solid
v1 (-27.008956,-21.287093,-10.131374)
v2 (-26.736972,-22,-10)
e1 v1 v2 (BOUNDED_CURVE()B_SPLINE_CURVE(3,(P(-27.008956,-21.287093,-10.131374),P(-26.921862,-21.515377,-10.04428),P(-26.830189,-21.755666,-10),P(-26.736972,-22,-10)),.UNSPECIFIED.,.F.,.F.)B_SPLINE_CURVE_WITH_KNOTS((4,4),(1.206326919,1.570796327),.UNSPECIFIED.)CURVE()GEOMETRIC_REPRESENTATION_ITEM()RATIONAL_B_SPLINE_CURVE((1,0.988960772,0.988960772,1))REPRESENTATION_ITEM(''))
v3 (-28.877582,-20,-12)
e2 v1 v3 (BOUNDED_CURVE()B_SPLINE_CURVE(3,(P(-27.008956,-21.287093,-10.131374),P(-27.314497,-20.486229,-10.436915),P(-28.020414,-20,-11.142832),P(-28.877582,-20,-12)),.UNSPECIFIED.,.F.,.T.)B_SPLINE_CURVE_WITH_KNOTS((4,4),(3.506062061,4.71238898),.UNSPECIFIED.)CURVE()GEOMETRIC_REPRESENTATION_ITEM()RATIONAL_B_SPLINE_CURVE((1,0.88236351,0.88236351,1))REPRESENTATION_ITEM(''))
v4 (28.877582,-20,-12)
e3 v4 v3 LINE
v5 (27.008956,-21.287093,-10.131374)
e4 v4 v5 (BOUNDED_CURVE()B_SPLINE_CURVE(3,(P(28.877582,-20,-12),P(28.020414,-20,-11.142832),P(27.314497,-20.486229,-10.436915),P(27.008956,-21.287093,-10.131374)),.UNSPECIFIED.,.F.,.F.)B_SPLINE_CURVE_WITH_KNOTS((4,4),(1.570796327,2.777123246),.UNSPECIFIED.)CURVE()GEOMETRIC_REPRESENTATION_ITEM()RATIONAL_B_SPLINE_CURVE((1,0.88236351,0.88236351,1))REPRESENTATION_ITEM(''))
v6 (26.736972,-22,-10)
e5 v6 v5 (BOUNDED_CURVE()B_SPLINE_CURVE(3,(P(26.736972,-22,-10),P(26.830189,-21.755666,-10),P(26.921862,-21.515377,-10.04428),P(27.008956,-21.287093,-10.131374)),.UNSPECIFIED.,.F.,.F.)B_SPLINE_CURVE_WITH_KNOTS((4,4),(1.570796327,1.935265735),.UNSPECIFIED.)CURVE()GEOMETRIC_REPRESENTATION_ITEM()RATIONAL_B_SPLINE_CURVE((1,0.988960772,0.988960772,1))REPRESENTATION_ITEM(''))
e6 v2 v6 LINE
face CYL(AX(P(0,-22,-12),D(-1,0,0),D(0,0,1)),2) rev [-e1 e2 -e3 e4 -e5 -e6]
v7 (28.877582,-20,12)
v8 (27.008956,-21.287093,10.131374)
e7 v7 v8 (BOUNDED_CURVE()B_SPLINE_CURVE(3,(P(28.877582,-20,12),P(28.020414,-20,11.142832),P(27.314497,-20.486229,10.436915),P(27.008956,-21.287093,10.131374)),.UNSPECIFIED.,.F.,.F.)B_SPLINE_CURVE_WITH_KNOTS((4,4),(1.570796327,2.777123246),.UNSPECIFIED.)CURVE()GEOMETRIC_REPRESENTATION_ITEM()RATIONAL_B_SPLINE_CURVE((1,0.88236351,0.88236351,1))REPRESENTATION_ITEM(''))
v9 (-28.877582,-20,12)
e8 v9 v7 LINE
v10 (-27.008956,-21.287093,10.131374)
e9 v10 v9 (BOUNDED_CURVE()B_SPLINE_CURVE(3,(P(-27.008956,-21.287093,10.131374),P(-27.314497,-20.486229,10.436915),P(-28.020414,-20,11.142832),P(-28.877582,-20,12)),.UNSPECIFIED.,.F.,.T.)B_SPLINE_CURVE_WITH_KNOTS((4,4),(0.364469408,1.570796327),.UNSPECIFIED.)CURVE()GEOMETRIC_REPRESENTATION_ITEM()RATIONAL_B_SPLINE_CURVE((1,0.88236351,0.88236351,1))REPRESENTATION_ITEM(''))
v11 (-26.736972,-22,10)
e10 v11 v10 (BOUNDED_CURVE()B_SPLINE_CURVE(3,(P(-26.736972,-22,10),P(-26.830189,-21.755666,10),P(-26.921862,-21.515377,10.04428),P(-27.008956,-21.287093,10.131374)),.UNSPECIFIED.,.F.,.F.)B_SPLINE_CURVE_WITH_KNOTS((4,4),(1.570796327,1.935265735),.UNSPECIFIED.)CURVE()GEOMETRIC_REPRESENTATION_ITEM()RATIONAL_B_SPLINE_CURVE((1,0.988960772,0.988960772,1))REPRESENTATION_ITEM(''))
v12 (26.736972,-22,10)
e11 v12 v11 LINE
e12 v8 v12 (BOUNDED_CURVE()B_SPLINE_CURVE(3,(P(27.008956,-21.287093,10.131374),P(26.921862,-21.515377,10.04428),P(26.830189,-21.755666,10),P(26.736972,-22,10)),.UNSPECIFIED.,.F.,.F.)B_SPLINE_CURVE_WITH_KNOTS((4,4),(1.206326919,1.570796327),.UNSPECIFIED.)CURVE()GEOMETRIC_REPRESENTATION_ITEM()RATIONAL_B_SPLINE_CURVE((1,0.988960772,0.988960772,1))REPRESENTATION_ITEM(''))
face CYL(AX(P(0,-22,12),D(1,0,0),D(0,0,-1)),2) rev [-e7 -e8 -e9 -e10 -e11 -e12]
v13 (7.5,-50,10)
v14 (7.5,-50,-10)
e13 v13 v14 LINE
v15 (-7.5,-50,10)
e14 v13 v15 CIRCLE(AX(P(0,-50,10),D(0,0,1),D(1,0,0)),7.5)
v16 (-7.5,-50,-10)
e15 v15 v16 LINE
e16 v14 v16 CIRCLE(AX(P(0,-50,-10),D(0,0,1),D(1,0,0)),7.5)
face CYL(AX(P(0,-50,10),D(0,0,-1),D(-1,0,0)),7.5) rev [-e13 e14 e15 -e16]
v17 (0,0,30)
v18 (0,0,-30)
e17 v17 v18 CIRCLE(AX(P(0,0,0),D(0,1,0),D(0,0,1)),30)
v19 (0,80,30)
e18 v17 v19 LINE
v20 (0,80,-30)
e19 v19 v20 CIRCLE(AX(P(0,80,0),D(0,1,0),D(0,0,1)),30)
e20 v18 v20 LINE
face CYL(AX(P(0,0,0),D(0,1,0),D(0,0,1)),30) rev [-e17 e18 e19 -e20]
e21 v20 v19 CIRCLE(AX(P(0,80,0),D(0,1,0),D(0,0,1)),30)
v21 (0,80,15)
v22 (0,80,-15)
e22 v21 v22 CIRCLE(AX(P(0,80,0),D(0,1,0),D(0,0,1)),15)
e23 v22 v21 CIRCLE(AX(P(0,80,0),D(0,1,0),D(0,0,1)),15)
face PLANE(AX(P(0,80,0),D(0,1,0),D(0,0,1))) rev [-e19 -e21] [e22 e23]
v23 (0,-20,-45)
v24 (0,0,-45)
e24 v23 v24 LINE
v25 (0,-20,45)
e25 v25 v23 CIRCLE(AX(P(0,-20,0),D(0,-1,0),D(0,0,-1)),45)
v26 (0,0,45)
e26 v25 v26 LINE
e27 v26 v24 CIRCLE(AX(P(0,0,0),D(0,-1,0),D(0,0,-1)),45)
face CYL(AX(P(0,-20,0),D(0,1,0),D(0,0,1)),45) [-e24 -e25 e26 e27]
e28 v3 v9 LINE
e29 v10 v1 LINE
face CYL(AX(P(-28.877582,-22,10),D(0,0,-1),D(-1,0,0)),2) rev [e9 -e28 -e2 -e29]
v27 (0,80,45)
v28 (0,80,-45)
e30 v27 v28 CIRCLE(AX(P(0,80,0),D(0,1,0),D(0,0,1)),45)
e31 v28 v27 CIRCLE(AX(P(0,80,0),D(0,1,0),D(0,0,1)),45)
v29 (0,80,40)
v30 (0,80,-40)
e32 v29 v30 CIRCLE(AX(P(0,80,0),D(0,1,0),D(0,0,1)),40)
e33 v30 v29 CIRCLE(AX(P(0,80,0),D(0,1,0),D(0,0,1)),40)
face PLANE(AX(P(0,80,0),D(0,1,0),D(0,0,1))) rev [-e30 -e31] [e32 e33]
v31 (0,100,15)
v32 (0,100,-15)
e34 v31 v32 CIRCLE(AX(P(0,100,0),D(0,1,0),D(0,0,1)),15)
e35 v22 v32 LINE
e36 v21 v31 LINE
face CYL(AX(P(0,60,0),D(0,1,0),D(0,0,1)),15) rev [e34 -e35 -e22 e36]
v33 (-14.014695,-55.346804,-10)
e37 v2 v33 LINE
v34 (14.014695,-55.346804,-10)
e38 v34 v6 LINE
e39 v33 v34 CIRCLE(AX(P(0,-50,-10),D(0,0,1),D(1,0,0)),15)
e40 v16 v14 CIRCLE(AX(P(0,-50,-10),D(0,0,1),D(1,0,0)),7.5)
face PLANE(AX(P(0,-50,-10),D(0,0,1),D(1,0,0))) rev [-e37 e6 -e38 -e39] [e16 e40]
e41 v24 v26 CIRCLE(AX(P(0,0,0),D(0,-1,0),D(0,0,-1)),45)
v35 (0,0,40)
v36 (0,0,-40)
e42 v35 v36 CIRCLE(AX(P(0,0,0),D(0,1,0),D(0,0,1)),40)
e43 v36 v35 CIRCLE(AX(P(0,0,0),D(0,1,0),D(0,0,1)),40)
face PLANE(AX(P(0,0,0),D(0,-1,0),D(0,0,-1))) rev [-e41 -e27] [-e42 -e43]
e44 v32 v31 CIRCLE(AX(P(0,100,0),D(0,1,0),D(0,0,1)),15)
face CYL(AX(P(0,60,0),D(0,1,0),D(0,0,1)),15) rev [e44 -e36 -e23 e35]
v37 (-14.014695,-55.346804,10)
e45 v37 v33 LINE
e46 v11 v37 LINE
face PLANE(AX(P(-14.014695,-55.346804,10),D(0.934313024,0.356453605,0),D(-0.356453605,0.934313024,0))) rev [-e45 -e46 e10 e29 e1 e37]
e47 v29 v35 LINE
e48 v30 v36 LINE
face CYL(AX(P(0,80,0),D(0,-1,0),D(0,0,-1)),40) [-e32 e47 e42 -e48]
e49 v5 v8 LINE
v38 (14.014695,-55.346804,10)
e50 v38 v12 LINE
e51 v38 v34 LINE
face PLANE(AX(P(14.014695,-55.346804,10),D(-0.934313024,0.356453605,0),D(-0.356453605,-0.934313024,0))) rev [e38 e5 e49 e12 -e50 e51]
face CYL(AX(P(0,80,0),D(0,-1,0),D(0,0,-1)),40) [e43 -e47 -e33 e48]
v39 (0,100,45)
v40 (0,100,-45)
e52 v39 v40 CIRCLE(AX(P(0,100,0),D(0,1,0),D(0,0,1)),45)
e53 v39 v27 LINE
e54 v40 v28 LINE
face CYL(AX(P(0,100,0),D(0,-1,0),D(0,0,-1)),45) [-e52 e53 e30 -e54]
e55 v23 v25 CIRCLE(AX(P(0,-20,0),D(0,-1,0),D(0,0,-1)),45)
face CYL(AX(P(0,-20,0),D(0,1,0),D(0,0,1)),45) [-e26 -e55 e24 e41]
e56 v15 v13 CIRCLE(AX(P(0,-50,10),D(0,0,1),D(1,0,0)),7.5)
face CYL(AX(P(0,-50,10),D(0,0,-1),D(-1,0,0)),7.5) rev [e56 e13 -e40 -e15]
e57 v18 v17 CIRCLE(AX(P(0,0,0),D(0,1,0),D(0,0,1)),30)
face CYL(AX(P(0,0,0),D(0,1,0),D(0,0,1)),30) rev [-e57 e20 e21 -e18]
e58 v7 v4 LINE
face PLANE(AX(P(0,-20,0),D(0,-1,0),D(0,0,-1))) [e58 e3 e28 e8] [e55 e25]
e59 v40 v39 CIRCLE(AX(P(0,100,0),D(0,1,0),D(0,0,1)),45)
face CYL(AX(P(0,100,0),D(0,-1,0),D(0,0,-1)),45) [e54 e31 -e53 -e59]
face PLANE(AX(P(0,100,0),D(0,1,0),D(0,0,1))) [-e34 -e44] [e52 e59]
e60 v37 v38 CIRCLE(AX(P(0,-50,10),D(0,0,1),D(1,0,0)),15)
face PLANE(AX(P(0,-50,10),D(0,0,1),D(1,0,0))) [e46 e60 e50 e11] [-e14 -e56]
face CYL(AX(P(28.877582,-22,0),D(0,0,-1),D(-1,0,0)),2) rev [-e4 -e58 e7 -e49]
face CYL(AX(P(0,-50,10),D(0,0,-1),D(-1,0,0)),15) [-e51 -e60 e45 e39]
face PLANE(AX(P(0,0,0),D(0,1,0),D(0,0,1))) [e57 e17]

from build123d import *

# Parameters (mm, degrees)
SKETCH_1_R          = 40
EXTRUDE_1_DEPTH     = 80
SKETCH_2_R          = 45
EXTRUDE_2_DEPTH     = 20
EXTRUDE_START       = 20
SKETCH_3_R          = 45
EXTRUDE_3_DEPTH     = 20
CUT_EXTRUDE_START   = -20
SKETCH_4_R          = 30
CUT_EXTRUDE_2_DEPTH = 80
SKETCH_5_R          = 15
CUT_EXTRUDE_3_DEPTH = 40
SKETCH_6_R          = 7.5
EXTRUDE_4_DEPTH     = 10
FILLET_1_R          = 2


with BuildPart() as part:
    # 草图1 → 凸台-拉伸1 (new body)
    with BuildSketch(Plane(origin=(0, 0, 0), x_dir=(1, 0, 0), z_dir=(0, 1, 0))):
        with Locations(Location((0, 0, 0), (0, 0, 270))):
            Circle(SKETCH_1_R)
    extrude(amount=EXTRUDE_1_DEPTH)

    # 草图2 → 凸台-拉伸2 (add)
    with BuildSketch(Plane.XZ):
        with Locations(Location((0, 0, 0), (0, 0, 270))):
            Circle(SKETCH_2_R)
    extrude(amount=EXTRUDE_2_DEPTH)

    # 草图3 → 凸台-拉伸3 (add)
    with BuildSketch(Plane(origin=(0, 80, 0), x_dir=(1, 0, 0), z_dir=(0, 1, 0)).offset(EXTRUDE_START)):
        with Locations(Location((0, 0, 0), (0, 0, 90))):
            Circle(SKETCH_3_R)
    extrude(amount=-EXTRUDE_3_DEPTH)

    # 草图4 → 切除-拉伸2 (cut)
    with BuildSketch(Plane(origin=(0, 100, 0), x_dir=(1, 0, 0), z_dir=(0, 1, 0)).offset(CUT_EXTRUDE_START)):
        with Locations(Location((0, 0, 0), (0, 0, 270))):
            Circle(SKETCH_4_R)
    extrude(amount=-CUT_EXTRUDE_2_DEPTH, mode=Mode.SUBTRACT)

    # 草图5 → 切除-拉伸3 (cut)
    with BuildSketch(Plane(origin=(0, 100, 0), x_dir=(1, 0, 0), z_dir=(0, 1, 0))):
        with Locations(Location((0, 0, 0), (0, 0, 270))):
            Circle(SKETCH_5_R)
    extrude(amount=-CUT_EXTRUDE_3_DEPTH, mode=Mode.SUBTRACT)

    # 草图6 → 凸台-拉伸4 (add, symmetric)
    with BuildSketch(Plane.XY):
        with BuildLine():
            Line((-14.014695363, -55.346804082), (-27.5, -20))
            Line((-27.5, -20), (27.5, -20))
            Line((27.5, -20), (14.014695363, -55.346804082))
            ThreePointArc((14.014695363, -55.346804082), (0, -65), (-14.014695363, -55.346804082))
        make_face()
        with Locations((0, -50)):
            Circle(SKETCH_6_R, mode=Mode.SUBTRACT)
    extrude(amount=EXTRUDE_4_DEPTH, both=True)

    # 圆角1
    fillet_1_edges = [part.edges().sort_by_distance(p)[0] for p in [
        (0, -20, 10),
        (0, -20, -10),
        (27.5, -20, 0),
        (-27.5, -20, 0),
    ]]
    fillet(fillet_1_edges, radius=FILLET_1_R)


solid = part.part
